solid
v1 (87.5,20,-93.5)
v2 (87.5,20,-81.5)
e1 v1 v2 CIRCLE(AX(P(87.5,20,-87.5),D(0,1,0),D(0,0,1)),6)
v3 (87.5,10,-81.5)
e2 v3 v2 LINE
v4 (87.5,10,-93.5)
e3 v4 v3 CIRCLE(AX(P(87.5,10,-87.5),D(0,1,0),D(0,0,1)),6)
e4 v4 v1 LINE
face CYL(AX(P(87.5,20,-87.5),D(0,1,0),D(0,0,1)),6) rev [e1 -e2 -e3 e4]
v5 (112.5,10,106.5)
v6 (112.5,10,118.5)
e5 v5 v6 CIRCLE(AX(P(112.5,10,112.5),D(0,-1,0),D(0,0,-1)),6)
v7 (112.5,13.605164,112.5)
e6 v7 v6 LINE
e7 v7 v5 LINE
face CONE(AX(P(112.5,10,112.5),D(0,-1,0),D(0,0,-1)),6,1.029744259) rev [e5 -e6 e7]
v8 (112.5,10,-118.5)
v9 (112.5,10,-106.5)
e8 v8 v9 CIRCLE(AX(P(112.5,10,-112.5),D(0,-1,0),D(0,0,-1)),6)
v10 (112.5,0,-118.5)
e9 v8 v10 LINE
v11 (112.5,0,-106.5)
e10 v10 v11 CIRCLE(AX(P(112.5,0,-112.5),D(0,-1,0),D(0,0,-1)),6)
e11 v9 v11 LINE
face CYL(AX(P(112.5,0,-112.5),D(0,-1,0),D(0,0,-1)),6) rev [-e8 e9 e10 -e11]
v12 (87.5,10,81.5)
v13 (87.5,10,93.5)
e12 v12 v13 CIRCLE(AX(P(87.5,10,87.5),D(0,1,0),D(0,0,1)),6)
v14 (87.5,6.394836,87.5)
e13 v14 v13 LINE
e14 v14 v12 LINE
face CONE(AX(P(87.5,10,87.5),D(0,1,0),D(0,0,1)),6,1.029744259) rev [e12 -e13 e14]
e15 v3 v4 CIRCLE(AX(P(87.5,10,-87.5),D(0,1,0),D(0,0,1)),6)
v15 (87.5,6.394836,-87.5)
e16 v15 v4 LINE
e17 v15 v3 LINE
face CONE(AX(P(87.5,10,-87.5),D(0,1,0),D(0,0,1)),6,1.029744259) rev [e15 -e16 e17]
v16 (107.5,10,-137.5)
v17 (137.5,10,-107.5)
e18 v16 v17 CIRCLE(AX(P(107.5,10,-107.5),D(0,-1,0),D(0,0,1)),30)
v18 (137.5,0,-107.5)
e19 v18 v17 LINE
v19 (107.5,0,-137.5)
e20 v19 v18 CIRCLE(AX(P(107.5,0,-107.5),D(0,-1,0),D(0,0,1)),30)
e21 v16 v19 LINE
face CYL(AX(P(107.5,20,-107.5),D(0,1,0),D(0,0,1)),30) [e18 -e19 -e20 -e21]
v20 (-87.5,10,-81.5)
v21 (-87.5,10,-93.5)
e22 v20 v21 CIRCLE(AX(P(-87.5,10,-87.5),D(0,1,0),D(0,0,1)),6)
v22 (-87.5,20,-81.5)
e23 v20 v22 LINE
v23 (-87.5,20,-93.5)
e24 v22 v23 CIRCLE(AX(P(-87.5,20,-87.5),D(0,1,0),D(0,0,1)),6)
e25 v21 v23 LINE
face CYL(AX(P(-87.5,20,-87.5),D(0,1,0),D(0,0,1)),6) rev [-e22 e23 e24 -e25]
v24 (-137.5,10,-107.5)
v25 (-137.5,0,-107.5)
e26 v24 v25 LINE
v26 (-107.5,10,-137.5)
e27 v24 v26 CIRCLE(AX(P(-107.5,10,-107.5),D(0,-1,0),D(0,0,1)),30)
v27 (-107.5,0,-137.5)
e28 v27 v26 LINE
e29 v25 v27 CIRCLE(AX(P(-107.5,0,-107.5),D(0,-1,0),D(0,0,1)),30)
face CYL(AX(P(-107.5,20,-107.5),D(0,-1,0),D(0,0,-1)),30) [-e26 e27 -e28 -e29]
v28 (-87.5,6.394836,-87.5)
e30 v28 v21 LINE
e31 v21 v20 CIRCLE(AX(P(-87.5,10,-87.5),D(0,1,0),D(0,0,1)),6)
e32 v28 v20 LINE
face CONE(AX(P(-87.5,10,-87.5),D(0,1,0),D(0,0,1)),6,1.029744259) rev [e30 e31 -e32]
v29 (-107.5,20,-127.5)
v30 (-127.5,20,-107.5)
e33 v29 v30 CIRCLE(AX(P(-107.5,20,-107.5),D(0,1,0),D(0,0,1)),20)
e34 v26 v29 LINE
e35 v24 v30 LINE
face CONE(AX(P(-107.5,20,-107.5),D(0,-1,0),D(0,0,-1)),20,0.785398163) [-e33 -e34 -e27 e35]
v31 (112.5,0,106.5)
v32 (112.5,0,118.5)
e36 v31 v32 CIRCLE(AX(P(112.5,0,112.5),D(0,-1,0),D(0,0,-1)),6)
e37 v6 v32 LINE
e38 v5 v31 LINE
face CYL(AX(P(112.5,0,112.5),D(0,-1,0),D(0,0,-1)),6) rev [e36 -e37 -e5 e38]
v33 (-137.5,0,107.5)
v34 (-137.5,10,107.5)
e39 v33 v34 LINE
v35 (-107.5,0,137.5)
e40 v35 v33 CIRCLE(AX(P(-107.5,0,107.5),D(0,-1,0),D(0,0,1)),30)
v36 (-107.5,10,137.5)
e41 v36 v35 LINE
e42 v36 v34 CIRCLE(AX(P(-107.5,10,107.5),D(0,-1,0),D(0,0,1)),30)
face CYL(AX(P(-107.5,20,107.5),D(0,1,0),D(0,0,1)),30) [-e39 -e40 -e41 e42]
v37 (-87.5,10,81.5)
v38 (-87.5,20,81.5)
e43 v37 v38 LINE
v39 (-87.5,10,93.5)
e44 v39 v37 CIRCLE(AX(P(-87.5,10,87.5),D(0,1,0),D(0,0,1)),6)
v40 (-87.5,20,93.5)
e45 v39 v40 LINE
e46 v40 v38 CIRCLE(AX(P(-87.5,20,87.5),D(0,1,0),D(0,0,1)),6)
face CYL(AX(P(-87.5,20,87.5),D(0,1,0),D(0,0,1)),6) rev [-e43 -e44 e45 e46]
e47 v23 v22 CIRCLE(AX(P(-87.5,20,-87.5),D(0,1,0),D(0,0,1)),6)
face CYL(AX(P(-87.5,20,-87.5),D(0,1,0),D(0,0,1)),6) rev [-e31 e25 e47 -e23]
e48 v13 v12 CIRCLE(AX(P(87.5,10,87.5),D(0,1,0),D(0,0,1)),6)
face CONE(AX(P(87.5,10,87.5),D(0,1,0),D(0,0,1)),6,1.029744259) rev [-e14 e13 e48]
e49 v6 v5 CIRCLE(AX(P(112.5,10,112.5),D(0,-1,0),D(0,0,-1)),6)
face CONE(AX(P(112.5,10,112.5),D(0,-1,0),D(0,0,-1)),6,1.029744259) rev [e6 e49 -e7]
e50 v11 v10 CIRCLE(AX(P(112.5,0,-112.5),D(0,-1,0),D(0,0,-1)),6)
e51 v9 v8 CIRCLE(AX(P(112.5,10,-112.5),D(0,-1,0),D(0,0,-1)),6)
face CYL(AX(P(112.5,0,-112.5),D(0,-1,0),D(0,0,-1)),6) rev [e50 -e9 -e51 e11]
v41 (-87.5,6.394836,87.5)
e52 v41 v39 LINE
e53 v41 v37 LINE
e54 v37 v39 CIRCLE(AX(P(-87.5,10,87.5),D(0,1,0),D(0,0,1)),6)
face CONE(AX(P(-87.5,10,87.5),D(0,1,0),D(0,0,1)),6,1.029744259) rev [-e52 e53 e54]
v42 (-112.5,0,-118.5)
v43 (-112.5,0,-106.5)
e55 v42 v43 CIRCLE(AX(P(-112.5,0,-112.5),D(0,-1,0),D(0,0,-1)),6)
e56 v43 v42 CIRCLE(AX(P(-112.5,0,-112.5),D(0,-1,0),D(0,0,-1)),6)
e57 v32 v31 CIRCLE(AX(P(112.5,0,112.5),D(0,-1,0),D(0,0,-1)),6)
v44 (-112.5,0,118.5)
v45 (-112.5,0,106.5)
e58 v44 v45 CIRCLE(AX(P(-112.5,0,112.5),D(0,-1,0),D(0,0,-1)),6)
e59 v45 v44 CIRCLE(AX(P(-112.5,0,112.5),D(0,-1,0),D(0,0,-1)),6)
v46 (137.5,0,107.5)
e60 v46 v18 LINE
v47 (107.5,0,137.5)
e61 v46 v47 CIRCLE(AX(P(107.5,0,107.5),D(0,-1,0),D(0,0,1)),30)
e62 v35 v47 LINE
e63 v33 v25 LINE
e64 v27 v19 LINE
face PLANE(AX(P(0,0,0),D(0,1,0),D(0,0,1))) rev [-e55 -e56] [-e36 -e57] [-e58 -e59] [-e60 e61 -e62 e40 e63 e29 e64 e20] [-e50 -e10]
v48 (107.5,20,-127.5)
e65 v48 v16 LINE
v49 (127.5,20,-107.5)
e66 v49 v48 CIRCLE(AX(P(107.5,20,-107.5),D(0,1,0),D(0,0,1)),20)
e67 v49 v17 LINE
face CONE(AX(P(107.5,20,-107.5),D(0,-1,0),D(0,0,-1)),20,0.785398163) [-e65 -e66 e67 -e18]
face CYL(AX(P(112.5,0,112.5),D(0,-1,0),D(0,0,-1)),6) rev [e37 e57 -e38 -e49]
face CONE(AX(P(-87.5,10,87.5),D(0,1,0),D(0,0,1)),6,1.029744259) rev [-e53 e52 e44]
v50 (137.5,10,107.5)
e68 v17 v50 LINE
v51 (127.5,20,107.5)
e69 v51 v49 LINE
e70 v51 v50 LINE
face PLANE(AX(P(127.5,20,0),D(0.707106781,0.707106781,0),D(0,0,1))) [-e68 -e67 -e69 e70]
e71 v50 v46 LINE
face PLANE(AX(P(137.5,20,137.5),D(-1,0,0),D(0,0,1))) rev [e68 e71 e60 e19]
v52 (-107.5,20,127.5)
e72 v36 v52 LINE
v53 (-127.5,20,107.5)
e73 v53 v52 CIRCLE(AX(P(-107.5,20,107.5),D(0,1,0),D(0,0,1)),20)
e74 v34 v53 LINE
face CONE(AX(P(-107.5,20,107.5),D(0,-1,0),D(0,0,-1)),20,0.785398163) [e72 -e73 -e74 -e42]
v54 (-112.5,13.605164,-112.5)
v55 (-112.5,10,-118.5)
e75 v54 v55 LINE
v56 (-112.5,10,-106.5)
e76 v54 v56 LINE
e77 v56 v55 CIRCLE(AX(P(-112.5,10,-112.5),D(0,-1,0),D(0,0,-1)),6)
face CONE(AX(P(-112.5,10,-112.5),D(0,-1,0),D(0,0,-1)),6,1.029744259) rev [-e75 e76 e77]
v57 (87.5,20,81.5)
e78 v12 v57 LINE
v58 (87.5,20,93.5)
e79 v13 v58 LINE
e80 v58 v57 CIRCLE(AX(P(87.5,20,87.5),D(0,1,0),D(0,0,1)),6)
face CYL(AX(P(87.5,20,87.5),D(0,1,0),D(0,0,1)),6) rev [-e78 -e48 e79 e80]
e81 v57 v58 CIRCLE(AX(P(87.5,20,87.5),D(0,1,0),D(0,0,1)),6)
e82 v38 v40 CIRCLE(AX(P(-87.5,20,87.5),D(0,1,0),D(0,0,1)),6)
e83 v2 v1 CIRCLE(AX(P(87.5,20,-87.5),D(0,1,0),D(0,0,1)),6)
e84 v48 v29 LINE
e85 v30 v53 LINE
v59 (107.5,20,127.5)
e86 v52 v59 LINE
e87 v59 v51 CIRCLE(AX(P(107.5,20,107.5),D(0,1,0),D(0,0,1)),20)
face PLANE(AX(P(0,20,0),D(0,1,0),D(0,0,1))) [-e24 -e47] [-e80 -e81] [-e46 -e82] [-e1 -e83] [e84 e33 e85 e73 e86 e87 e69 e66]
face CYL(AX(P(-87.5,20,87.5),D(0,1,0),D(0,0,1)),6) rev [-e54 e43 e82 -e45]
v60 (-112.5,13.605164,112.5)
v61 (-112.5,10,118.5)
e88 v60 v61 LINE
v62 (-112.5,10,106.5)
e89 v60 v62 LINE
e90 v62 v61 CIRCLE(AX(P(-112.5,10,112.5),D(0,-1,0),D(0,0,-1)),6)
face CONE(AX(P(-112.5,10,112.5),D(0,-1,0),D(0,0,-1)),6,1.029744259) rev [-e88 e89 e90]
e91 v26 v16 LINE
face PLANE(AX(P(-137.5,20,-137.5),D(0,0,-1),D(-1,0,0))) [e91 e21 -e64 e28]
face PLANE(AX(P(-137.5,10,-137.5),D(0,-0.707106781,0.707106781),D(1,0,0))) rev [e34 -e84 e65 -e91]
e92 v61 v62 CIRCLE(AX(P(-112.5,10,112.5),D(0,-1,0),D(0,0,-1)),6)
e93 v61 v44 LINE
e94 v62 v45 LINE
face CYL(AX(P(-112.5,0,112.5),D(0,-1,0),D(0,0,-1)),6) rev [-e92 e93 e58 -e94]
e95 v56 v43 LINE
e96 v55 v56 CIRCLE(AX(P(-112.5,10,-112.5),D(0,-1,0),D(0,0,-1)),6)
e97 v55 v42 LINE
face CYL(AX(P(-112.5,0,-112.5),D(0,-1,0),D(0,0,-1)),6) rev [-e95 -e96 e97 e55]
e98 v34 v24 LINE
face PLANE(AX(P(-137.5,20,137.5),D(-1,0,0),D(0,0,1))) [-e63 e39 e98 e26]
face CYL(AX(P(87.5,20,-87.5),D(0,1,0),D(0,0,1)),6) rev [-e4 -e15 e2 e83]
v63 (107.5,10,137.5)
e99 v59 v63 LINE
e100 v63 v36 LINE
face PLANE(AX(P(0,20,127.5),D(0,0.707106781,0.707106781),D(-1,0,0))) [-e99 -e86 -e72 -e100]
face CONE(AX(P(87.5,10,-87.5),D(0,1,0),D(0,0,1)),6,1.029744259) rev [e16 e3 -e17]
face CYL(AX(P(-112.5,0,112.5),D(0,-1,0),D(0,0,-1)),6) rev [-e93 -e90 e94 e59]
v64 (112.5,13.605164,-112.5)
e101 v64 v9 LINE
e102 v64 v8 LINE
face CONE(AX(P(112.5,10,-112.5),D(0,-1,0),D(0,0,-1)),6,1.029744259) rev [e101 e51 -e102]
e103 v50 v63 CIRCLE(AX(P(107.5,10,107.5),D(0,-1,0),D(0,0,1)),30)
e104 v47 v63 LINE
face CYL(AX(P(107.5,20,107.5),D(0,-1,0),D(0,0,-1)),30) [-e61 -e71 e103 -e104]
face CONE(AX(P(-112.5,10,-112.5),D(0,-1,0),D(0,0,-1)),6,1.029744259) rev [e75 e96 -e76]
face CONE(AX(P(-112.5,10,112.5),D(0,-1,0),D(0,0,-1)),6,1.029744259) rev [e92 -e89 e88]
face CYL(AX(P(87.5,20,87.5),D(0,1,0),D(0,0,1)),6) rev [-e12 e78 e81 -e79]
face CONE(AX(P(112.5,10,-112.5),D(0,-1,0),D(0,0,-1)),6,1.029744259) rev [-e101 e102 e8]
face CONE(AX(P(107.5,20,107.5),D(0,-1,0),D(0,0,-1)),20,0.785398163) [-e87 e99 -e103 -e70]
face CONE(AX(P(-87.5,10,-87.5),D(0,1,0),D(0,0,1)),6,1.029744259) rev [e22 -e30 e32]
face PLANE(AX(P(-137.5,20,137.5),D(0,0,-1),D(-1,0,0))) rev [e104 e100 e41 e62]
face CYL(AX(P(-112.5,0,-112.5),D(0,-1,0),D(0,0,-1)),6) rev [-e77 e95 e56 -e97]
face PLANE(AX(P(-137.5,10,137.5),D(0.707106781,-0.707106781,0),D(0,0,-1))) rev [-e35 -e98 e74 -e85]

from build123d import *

# Parameters (mm, degrees)
BASE_PLATE_PROFILE_275X275_W       = 275
BASE_PLATE_PROFILE_275X275_H       = 275
BASE_PLATE_275X275X20_DEPTH        = 20
CORNER_FILLETS_R30_R               = 30
EDGE_CHAMFER_10X45_SIZE            = 10
DOWEL_HOLES_12_ON_175_SQUARE_D     = 12
DOWEL_HOLES_12_ON_175_SQUARE_DEPTH = 10
DOWEL_HOLES_12_ON_175_SQUARE_TIP   = 3.605163714
DOWEL_HOLES_12_ON_225_SQUARE_D     = 12
DOWEL_HOLES_12_ON_225_SQUARE_DEPTH = 10
DOWEL_HOLES_12_ON_225_SQUARE_TIP   = 3.605163714


with BuildPart() as part:
    # Base Plate Profile 275x275 → Base Plate 275x275x20 (new body)
    with BuildSketch(Plane(origin=(0, 0, 0), x_dir=(1, 0, 0), z_dir=(0, 1, 0))):
        Rectangle(BASE_PLATE_PROFILE_275X275_W, BASE_PLATE_PROFILE_275X275_H)
    extrude(amount=BASE_PLATE_275X275X20_DEPTH)

    # Corner Fillets R30
    corner_fillets_r30_edges = [part.edges().sort_by_distance(p)[0] for p in [
        (-137.5, 10, 137.5),
        (-137.5, 10, -137.5),
        (137.5, 10, -137.5),
        (137.5, 10, 137.5),
    ]]
    fillet(corner_fillets_r30_edges, radius=CORNER_FILLETS_R30_R)

    # Edge Chamfer 10x45
    edge_chamfer_10x45_edges = [part.edges().sort_by_distance(p)[0] for p in [
        (0, 20, -137.5),
        (137.5, 20, 0),
        (0, 20, 137.5),
        (-137.5, 20, 0),
        (-128.713203436, 20, 128.713203436),
        (128.713203436, 20, 128.713203436),
        (-128.713203436, 20, -128.713203436),
        (128.713203436, 20, -128.713203436),
    ]]
    chamfer(edge_chamfer_10x45_edges, length=EDGE_CHAMFER_10X45_SIZE)

    # Dowel Holes Ø12 on 175 Square
    with Locations(Plane(origin=(-87.5, 20, -87.5), x_dir=(0, 0, 1), z_dir=(0, 1, 0))):
        with Locations((0, 0), (0, 175), (175, 175), (175, 0)):
            Hole(DOWEL_HOLES_12_ON_175_SQUARE_D / 2, depth=DOWEL_HOLES_12_ON_175_SQUARE_DEPTH)
            with Locations((0, 0, -(DOWEL_HOLES_12_ON_175_SQUARE_DEPTH + DOWEL_HOLES_12_ON_175_SQUARE_TIP / 2))):  # 118° drill point
                Cone(0, DOWEL_HOLES_12_ON_175_SQUARE_D / 2, DOWEL_HOLES_12_ON_175_SQUARE_TIP, mode=Mode.SUBTRACT)

    # Dowel Holes Ø12 on 225 Square
    with Locations(Plane(origin=(-112.5, 0, 112.5), x_dir=(0, 0, -1), z_dir=(0, -1, 0))):
        with Locations((0, 0), (0, 225), (225, 225), (225, 0)):
            Hole(DOWEL_HOLES_12_ON_225_SQUARE_D / 2, depth=DOWEL_HOLES_12_ON_225_SQUARE_DEPTH)
            with Locations((0, 0, -(DOWEL_HOLES_12_ON_225_SQUARE_DEPTH + DOWEL_HOLES_12_ON_225_SQUARE_TIP / 2))):  # 118° drill point
                Cone(0, DOWEL_HOLES_12_ON_225_SQUARE_D / 2, DOWEL_HOLES_12_ON_225_SQUARE_TIP, mode=Mode.SUBTRACT)


solid = part.part
